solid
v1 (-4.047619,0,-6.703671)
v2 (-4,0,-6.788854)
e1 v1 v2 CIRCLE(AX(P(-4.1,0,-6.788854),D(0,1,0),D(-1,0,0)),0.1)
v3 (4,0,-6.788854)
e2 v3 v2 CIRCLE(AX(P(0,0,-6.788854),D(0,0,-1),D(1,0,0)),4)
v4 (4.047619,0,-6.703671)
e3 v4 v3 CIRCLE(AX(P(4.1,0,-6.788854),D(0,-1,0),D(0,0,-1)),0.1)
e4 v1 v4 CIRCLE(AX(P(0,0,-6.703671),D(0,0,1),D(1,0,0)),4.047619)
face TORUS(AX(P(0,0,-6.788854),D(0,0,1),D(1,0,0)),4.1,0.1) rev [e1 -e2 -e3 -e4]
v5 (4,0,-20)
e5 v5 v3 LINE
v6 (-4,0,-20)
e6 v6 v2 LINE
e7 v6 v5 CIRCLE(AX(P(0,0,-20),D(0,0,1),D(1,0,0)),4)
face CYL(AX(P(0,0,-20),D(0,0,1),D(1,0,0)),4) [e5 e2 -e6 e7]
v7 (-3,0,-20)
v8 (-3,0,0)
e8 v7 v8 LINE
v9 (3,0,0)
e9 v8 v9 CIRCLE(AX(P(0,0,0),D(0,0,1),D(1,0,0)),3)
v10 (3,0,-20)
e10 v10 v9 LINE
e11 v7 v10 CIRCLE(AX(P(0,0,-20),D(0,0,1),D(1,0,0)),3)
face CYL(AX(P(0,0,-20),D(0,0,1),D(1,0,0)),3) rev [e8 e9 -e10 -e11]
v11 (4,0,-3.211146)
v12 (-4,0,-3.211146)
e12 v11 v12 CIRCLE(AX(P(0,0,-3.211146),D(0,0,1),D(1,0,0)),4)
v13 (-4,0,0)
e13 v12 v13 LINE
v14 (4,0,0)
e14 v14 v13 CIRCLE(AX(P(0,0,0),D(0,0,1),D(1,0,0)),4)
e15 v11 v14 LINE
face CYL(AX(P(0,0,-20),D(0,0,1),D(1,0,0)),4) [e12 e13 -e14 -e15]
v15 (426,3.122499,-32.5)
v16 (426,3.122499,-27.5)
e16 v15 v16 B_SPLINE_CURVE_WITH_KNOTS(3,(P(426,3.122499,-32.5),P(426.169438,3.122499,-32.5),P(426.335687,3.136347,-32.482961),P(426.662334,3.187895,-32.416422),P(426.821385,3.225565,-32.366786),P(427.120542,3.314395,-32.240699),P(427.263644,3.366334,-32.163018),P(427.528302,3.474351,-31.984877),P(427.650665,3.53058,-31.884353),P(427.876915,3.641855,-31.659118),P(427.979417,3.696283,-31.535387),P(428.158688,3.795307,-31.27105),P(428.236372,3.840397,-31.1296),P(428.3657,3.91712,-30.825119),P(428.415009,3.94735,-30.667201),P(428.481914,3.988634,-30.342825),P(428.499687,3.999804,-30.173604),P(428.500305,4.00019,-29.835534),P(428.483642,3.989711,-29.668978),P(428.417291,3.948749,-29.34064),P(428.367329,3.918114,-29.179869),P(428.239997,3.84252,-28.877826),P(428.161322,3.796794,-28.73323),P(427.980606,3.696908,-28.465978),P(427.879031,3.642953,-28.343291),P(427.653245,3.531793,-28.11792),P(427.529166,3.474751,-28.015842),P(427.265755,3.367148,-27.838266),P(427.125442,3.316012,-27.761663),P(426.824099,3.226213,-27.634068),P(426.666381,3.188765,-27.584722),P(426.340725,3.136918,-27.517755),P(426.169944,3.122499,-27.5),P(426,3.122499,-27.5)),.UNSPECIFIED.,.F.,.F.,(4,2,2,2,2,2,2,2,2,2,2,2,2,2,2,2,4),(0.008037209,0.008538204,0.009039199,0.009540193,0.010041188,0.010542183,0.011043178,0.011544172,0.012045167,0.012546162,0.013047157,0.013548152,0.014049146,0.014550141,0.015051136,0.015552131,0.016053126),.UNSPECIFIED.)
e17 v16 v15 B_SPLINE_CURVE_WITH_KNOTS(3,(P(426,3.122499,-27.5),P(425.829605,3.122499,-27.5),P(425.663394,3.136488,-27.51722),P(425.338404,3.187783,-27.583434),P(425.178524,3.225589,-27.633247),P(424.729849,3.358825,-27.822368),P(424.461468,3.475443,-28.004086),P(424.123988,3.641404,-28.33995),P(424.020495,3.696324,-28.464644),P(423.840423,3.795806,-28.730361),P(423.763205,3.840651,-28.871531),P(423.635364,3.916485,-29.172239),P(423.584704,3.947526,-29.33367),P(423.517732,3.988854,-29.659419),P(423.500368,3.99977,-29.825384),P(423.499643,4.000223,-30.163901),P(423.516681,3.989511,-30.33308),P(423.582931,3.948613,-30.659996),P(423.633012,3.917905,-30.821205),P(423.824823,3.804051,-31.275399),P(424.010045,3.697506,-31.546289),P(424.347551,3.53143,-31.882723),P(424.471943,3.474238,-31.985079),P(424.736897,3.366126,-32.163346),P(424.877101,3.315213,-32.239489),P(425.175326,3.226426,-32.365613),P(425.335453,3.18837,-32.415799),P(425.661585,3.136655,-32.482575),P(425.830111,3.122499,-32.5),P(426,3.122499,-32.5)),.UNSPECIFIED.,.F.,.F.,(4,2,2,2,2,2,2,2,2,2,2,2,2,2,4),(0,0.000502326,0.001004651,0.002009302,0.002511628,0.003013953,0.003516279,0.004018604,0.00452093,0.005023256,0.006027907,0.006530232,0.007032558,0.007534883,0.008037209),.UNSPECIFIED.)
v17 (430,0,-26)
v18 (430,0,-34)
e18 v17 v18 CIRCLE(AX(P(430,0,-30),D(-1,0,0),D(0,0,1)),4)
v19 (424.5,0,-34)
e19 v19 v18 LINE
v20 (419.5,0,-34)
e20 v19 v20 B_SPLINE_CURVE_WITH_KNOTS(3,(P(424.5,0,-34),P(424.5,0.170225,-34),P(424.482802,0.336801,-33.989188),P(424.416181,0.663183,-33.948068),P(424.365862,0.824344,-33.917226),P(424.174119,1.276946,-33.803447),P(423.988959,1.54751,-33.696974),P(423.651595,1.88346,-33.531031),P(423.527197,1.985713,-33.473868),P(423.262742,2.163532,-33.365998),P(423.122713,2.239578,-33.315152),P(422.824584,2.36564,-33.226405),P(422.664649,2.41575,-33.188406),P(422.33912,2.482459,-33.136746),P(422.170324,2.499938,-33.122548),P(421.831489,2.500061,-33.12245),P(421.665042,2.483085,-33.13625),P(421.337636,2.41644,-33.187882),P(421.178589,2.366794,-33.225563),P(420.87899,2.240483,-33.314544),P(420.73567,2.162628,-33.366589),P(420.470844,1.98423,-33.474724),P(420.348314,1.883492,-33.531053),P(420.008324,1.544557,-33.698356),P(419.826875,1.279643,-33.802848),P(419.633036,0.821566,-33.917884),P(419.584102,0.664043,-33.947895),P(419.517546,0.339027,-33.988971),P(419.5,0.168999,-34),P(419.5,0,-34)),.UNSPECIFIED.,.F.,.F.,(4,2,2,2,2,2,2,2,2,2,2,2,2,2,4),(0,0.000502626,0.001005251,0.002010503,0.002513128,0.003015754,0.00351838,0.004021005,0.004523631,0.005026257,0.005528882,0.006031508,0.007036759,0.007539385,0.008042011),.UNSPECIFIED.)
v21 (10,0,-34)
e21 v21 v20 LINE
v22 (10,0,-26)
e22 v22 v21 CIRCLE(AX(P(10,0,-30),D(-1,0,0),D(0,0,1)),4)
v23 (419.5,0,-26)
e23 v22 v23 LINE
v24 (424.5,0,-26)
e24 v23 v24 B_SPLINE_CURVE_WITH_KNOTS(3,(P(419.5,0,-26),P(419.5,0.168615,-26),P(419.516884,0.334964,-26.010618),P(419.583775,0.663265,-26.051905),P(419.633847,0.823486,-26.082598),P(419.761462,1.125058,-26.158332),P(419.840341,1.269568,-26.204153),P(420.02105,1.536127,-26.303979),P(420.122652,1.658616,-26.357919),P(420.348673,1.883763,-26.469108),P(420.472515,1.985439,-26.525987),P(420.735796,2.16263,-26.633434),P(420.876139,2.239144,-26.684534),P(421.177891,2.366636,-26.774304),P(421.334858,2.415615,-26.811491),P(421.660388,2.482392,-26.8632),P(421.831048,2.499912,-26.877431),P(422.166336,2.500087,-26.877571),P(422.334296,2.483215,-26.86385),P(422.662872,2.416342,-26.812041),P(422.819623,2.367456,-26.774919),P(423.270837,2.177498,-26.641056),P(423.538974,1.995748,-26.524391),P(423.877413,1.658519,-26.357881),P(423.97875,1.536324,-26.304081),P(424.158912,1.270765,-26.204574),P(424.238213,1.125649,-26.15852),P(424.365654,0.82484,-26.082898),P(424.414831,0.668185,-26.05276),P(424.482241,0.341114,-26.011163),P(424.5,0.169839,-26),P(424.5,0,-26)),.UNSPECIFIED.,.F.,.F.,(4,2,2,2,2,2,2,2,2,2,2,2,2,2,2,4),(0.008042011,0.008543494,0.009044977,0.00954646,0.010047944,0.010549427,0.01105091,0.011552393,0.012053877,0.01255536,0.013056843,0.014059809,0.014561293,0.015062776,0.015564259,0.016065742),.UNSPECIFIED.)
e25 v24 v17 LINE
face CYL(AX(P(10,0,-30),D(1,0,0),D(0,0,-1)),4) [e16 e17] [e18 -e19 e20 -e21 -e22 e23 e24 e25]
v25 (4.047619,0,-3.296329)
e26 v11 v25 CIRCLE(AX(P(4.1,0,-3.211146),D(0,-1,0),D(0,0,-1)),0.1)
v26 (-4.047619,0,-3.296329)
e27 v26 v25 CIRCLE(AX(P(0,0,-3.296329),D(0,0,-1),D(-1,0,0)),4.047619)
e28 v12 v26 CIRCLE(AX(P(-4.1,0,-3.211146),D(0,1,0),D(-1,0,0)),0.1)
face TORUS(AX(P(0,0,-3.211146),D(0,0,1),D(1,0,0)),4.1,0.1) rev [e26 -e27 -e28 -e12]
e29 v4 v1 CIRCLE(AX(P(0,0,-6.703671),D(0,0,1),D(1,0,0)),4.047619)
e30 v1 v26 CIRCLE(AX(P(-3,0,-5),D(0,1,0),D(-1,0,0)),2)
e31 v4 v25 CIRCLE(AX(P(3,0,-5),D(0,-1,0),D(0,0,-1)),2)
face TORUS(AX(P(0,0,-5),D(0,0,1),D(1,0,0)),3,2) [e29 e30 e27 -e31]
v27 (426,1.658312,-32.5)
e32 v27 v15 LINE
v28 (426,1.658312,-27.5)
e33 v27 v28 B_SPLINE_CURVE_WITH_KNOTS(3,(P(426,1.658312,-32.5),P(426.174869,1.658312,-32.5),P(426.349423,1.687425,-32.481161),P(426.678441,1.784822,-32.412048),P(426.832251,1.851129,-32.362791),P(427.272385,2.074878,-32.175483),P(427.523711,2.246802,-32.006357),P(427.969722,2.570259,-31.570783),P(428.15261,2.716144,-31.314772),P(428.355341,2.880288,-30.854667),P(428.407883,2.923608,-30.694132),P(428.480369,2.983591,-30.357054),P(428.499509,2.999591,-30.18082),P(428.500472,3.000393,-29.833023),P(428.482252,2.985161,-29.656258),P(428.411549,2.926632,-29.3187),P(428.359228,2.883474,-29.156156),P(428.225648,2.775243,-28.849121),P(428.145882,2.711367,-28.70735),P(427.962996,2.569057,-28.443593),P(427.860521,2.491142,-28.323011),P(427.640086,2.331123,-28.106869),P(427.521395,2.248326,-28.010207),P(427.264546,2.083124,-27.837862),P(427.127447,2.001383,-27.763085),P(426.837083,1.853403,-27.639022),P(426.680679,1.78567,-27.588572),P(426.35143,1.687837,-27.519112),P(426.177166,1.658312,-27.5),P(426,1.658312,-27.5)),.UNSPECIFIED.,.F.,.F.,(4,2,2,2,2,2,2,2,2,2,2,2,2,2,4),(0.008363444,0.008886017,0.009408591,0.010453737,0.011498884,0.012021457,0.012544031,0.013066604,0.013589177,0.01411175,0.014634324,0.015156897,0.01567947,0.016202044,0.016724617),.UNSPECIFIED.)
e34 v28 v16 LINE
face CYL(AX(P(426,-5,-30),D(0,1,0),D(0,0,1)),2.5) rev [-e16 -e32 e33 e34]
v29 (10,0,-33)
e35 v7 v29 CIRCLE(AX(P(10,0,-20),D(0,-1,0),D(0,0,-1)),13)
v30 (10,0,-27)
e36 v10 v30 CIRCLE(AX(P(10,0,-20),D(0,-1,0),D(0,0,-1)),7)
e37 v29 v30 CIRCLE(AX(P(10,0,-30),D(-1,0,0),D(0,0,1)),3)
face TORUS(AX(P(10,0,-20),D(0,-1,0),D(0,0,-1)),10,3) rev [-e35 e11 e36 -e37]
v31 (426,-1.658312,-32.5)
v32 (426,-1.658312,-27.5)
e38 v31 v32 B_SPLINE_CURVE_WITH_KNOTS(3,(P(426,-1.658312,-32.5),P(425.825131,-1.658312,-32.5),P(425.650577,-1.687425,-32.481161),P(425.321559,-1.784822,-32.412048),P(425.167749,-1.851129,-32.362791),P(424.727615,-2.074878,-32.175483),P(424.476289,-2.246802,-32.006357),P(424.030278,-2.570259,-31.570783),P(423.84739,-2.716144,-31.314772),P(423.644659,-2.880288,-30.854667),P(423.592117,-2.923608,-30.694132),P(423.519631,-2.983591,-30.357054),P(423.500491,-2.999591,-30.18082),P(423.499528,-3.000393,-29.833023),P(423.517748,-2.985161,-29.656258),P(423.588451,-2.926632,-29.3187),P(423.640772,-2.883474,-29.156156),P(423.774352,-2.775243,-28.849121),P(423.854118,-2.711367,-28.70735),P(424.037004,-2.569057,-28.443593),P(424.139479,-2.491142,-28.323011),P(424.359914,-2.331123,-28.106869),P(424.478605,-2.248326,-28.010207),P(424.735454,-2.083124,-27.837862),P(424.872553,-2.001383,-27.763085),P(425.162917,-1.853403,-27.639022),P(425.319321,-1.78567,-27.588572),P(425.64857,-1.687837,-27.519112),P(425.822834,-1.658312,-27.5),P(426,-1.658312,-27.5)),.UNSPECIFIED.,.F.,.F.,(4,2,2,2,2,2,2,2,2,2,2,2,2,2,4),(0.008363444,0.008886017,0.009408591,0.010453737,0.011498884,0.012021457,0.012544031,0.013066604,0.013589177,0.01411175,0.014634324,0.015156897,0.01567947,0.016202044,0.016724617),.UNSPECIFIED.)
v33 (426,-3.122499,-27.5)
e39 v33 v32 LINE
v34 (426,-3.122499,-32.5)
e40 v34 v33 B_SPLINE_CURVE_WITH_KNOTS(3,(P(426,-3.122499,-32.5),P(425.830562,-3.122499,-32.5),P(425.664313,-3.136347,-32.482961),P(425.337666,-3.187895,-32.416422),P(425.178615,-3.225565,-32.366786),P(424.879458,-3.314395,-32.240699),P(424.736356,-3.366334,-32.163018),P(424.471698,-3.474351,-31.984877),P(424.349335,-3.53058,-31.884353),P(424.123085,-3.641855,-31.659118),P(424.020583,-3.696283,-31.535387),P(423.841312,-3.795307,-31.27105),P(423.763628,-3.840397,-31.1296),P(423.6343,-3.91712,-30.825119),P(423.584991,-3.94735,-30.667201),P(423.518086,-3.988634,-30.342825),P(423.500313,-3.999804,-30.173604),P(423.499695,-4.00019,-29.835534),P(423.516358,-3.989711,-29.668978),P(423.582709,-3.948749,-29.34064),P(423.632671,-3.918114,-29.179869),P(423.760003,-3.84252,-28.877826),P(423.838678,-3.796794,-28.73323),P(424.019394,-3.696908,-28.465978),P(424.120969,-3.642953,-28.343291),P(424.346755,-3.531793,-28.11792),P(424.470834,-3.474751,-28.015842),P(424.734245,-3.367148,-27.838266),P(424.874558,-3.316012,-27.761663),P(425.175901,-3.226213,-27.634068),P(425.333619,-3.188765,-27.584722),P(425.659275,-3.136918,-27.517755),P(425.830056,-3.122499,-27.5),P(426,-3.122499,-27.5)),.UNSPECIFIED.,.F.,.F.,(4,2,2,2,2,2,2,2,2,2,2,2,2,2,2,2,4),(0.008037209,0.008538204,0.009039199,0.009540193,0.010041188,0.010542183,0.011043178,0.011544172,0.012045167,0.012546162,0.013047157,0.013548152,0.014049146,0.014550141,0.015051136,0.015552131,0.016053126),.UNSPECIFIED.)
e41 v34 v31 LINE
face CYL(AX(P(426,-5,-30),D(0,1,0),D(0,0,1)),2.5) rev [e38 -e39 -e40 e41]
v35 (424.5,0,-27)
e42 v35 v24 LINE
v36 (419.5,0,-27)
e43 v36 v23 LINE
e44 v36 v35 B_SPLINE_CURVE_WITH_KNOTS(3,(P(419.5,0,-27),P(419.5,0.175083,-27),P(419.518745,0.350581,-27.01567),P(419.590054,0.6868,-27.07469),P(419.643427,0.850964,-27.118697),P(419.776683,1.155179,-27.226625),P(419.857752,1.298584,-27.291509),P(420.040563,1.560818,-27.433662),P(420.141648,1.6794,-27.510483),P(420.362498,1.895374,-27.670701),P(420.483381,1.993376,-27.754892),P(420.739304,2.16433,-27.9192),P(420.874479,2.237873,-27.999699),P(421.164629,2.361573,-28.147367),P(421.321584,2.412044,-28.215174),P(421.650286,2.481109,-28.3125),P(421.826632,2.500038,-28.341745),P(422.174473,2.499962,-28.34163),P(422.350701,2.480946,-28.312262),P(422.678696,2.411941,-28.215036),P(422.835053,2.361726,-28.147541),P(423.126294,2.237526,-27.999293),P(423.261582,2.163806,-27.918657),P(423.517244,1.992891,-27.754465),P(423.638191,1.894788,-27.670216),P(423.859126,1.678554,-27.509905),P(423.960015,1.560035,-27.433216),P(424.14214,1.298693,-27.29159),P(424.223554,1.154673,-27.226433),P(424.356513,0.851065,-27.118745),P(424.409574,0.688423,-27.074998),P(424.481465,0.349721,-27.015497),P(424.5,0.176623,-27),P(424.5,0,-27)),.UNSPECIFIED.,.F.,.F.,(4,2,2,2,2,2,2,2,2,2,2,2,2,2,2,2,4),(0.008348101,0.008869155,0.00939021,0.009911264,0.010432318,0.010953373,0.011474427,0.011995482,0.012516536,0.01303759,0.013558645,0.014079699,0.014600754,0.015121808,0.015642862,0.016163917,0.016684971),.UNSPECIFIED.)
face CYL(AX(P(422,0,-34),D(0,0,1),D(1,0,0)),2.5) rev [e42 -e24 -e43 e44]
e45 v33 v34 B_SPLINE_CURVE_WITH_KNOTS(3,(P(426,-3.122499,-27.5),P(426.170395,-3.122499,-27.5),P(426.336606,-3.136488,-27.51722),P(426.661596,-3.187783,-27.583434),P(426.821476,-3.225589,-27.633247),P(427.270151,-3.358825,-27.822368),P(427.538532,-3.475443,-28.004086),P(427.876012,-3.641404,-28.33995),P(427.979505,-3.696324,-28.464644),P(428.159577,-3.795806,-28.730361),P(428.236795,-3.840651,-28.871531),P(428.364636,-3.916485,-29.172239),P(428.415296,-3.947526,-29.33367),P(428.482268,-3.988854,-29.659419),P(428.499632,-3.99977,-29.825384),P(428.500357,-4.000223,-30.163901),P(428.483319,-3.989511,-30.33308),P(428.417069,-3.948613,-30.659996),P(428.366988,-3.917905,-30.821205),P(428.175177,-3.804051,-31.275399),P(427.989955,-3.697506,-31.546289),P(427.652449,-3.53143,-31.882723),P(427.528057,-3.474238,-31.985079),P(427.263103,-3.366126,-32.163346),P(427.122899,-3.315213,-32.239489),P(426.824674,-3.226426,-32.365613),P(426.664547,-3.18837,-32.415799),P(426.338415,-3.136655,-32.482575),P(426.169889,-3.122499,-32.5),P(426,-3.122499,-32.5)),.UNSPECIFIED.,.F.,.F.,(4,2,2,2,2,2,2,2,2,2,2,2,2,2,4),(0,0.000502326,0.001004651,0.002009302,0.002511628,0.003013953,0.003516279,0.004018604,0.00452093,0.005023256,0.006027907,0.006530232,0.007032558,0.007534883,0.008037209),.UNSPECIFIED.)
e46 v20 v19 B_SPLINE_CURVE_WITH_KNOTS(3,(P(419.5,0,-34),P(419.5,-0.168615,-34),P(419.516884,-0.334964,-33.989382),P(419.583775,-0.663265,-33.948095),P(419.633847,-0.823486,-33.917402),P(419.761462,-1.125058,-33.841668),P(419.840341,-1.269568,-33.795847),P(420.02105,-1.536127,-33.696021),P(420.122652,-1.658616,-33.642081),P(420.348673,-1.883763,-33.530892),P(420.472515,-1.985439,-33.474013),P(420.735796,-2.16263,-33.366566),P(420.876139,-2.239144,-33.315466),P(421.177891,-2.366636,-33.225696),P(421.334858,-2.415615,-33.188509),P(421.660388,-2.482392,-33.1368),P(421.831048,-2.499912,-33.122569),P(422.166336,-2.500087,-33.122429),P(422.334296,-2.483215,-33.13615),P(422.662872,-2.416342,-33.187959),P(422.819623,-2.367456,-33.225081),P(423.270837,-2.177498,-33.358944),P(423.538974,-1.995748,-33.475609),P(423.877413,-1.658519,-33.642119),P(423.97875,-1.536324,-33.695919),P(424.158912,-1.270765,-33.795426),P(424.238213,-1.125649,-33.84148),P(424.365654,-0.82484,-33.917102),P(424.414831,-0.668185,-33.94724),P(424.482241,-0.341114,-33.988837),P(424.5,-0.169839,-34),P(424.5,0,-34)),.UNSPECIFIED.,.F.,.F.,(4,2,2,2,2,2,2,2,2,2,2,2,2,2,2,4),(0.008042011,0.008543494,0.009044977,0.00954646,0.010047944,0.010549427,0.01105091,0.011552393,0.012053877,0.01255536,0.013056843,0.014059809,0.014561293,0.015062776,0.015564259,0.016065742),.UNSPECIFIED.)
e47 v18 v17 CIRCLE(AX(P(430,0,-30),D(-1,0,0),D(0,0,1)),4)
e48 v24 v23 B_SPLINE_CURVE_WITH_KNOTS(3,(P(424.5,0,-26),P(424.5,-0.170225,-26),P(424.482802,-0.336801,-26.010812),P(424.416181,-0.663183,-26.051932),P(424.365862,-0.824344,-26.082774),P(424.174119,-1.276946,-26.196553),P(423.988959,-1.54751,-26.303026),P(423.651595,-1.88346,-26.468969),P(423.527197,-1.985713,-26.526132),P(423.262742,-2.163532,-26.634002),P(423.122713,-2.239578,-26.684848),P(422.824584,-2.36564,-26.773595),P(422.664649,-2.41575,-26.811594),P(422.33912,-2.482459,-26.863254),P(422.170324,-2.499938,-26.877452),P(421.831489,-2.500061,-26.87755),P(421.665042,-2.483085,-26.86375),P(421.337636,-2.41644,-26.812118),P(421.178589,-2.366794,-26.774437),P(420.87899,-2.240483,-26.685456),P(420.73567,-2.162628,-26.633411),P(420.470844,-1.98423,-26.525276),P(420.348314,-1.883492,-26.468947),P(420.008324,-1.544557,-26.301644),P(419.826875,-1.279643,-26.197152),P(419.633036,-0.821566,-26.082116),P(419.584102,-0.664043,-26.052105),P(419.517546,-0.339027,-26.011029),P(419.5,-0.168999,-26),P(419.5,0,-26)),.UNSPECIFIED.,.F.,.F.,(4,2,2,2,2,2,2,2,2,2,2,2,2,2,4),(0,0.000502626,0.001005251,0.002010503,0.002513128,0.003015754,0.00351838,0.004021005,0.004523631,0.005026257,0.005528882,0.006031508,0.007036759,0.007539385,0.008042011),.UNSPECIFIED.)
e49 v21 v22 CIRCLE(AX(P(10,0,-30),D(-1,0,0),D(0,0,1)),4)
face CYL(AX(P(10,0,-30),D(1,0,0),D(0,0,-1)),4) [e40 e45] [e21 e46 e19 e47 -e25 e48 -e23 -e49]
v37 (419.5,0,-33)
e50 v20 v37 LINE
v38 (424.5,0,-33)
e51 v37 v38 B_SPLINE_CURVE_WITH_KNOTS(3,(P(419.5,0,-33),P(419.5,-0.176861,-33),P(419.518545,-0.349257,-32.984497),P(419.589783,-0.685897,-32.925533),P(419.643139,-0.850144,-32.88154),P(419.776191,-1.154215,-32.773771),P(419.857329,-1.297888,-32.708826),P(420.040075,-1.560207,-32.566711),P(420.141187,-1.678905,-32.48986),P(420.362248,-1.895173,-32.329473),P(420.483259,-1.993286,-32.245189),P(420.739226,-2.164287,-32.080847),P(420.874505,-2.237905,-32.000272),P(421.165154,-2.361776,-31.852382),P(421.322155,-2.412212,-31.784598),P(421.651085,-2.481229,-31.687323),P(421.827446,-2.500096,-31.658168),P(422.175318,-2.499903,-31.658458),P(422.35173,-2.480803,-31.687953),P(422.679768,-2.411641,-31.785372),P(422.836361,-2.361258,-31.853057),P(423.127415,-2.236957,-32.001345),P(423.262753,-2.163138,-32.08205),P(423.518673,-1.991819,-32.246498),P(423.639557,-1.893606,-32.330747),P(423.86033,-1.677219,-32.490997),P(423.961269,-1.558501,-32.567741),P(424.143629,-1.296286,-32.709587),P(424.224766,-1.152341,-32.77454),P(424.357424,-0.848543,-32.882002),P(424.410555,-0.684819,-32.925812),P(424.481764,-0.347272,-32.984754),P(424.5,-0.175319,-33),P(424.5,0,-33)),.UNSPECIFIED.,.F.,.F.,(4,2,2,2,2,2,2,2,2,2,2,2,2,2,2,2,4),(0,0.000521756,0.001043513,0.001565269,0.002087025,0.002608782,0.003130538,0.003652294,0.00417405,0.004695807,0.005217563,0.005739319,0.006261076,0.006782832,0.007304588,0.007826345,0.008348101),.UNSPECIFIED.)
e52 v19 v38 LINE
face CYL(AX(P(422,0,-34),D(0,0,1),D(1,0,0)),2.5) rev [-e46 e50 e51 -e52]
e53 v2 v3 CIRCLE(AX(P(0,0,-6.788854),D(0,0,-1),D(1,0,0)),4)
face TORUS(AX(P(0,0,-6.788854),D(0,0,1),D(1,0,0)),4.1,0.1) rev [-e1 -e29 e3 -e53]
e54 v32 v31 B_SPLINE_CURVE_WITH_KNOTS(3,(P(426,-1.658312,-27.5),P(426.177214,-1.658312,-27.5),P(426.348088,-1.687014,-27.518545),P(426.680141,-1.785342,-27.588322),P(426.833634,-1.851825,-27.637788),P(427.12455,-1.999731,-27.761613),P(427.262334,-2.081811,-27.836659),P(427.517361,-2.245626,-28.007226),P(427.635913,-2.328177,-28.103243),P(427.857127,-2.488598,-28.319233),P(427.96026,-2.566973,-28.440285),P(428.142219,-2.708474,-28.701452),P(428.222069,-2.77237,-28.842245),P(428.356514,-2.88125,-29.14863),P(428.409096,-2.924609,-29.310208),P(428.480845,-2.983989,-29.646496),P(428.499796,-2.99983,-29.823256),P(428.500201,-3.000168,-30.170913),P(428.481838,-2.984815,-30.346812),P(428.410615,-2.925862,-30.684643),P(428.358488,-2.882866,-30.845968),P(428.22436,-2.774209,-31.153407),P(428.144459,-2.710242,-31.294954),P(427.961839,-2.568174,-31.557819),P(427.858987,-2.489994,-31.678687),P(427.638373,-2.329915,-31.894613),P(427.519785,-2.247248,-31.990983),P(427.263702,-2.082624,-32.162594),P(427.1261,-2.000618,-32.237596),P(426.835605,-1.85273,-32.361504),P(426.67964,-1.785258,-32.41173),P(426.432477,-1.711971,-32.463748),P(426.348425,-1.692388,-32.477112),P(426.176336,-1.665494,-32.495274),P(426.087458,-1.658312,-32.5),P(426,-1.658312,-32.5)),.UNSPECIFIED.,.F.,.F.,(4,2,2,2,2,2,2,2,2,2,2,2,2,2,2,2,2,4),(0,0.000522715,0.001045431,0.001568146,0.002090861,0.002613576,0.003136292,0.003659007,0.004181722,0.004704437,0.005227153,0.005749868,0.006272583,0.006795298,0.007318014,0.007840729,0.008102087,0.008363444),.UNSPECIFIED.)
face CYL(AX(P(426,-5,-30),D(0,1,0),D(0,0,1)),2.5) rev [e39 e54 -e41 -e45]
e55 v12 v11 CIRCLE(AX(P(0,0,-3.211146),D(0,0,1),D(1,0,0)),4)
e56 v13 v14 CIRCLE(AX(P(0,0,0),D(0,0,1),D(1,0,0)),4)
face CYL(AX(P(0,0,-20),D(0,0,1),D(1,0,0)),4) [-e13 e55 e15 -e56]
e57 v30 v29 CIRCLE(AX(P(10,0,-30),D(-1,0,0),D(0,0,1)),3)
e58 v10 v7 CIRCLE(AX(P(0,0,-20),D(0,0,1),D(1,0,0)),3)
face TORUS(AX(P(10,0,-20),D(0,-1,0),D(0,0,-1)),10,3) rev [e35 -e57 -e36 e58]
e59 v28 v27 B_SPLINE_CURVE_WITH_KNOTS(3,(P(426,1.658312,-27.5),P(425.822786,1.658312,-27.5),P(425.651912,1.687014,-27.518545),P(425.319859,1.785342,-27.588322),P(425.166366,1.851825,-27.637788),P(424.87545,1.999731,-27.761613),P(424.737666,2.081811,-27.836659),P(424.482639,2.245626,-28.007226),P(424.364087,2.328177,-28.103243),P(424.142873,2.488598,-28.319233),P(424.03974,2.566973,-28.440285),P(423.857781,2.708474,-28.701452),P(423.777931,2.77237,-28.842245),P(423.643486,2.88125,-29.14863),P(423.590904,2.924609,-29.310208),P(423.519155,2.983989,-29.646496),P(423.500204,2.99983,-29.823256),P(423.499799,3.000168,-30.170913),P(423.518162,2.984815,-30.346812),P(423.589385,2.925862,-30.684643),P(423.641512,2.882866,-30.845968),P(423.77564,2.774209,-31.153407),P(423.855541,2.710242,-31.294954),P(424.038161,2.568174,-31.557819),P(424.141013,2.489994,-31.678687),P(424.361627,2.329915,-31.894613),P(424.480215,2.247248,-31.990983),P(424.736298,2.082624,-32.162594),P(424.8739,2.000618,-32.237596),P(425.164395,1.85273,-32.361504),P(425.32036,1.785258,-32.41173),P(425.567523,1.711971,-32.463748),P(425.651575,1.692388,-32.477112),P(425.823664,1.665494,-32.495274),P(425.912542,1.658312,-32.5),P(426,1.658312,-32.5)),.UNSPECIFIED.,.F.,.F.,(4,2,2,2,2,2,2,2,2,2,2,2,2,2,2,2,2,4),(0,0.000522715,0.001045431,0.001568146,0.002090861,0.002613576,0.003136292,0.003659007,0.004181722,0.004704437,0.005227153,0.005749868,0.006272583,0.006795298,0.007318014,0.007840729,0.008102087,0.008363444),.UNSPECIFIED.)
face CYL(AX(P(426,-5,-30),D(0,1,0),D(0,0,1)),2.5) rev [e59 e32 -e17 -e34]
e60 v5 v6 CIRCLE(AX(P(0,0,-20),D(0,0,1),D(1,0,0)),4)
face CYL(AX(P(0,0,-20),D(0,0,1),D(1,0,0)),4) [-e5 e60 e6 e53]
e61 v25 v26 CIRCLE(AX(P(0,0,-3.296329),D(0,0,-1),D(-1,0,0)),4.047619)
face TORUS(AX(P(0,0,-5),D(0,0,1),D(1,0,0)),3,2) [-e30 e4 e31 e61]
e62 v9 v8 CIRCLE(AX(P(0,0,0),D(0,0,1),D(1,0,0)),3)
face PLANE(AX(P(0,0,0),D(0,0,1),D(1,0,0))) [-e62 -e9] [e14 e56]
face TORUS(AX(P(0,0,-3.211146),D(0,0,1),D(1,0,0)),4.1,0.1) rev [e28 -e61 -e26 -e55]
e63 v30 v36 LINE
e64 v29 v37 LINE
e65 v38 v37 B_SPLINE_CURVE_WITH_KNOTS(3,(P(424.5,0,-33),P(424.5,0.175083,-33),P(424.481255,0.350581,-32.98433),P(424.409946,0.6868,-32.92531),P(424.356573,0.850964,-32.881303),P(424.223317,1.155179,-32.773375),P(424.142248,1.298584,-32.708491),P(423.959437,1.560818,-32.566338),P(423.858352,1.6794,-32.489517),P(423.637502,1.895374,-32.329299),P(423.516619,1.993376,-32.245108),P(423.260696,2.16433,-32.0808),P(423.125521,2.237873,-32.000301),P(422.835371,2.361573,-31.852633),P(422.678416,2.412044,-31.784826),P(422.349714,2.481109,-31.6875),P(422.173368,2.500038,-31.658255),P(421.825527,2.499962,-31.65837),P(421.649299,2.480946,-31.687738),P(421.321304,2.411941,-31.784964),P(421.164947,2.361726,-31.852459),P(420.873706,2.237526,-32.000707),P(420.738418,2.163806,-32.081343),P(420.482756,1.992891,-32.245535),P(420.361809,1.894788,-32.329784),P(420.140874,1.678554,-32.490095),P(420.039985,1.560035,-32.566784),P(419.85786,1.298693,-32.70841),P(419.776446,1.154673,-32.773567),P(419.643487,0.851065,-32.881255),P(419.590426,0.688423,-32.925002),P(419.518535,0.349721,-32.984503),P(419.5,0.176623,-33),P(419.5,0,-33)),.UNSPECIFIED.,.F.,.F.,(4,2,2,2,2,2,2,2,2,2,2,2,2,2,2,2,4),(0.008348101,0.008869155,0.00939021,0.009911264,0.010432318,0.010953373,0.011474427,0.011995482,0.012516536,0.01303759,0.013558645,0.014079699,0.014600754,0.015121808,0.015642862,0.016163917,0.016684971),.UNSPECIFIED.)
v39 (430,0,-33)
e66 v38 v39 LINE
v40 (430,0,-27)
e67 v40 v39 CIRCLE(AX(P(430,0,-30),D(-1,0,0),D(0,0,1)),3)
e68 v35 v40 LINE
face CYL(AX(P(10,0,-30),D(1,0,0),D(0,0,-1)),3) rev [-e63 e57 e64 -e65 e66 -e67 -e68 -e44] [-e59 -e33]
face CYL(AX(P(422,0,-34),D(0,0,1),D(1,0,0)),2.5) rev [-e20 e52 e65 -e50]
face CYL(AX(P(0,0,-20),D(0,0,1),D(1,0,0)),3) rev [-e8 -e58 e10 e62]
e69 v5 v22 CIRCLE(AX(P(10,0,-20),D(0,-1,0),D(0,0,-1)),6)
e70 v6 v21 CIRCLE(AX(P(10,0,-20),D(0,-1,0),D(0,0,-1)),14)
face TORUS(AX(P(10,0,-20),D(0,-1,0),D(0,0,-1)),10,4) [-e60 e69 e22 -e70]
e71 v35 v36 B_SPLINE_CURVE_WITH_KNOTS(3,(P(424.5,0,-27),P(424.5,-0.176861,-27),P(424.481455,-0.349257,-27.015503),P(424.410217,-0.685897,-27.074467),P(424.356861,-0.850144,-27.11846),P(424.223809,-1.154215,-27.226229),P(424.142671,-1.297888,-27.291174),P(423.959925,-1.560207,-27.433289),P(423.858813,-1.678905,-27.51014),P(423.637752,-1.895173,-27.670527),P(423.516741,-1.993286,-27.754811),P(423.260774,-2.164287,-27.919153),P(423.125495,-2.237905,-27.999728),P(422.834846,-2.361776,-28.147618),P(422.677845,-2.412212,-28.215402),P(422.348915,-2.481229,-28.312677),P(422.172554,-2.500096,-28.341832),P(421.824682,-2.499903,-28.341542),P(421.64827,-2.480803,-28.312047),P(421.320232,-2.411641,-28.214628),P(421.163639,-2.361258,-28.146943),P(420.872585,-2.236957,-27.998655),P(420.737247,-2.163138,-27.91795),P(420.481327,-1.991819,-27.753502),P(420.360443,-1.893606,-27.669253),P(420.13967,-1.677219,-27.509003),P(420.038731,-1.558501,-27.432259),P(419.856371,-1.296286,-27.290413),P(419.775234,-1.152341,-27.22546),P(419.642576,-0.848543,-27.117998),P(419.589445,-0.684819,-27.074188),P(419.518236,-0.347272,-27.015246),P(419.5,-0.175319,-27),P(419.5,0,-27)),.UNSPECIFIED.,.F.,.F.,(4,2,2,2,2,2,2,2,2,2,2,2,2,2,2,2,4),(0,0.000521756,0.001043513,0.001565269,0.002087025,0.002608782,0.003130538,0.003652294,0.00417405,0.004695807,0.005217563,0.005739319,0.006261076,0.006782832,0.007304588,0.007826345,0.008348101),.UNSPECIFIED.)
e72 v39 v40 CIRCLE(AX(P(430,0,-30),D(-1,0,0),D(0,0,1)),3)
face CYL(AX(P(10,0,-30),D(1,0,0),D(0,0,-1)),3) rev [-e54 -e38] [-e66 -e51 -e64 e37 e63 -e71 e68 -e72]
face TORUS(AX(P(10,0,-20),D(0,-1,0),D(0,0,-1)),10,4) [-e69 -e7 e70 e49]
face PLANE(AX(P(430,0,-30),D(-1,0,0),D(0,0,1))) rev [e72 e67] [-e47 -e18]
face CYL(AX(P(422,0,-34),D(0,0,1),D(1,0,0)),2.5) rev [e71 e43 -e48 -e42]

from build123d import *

# Parameters (mm, degrees)
SKETCH1_R               = 4
SKETCH1_R_2             = 3
FILLET1_R               = 0.1
CUT_EXTRUDE1_DEPTH      = 432.371069971
CUT_EXTRUDE1_DEPTH_BACK = 432.371069971
SKETCH4_R               = 2.5
CUT_EXTRUDE2_DEPTH      = 432.371070071
CUT_EXTRUDE2_DEPTH_BACK = 432.371070071
SKETCH5_R               = 2.5


with BuildPart() as part:
    # Sweep1: sweep along a path in Sketch2
    with BuildLine(Plane(origin=(0, 0, 0), x_dir=(1, 0, 0), z_dir=(0, 1, 0))) as sweep1_path:
        Line((0, 0), (0, 20))
        ThreePointArc((0, 20), (2.928932188, 27.071067812), (10, 30))
        Line((10, 30), (430, 30))
    # Sketch1 → Sweep1 (sweep)
    with BuildSketch(Plane.XY):
        Circle(SKETCH1_R)
        Circle(SKETCH1_R_2, mode=Mode.SUBTRACT)
    sweep(path=sweep1_path.line)

    # Sketch3 → Revolve1 (revolve)
    with BuildSketch(Plane(origin=(0, 0, 0), x_dir=(1, 0, 0), z_dir=(0, 1, 0)), mode=Mode.PRIVATE) as revolve1_sk:
        with BuildLine():
            Line((-4, 6.732050808), (-4, 3.267949192))
            ThreePointArc((-4, 3.267949192), (-5, 5), (-4, 6.732050808))
        make_face()
    revolve(revolve1_sk.sketch.rotate(Axis((0, 0, 0), (0, 0, -1)), 180), axis=Axis((0, 0, 0), (0, 0, -1)))

    # Fillet1
    fillet1_edges = [part.edges().sort_by_distance(p)[0] for p in [
        (-4, 0, -6.732050808),
        (-4, 0, -3.267949192),
    ]]
    fillet(fillet1_edges, radius=FILLET1_R)

    # Sketch4 → Cut-Extrude1 (cut, two sides: drawn at the far end of the back side and taken through both)
    with BuildSketch(Plane(origin=(0, 0, 0), x_dir=(1, 0, 0), z_dir=(0, 1, 0)).offset(-CUT_EXTRUDE1_DEPTH_BACK)):
        with Locations(Location((426, 30, 0), (0, 0, 270))):
            Circle(SKETCH4_R)
    extrude(amount=CUT_EXTRUDE1_DEPTH + CUT_EXTRUDE1_DEPTH_BACK, mode=Mode.SUBTRACT)

    # Sketch5 → Cut-Extrude2 (cut, two sides: drawn at the far end of the back side and taken through both)
    with BuildSketch(Plane.XY.offset(-CUT_EXTRUDE2_DEPTH_BACK)):
        with Locations((422, 0)):
            Circle(SKETCH5_R)
    extrude(amount=CUT_EXTRUDE2_DEPTH + CUT_EXTRUDE2_DEPTH_BACK, mode=Mode.SUBTRACT)


solid = part.part
